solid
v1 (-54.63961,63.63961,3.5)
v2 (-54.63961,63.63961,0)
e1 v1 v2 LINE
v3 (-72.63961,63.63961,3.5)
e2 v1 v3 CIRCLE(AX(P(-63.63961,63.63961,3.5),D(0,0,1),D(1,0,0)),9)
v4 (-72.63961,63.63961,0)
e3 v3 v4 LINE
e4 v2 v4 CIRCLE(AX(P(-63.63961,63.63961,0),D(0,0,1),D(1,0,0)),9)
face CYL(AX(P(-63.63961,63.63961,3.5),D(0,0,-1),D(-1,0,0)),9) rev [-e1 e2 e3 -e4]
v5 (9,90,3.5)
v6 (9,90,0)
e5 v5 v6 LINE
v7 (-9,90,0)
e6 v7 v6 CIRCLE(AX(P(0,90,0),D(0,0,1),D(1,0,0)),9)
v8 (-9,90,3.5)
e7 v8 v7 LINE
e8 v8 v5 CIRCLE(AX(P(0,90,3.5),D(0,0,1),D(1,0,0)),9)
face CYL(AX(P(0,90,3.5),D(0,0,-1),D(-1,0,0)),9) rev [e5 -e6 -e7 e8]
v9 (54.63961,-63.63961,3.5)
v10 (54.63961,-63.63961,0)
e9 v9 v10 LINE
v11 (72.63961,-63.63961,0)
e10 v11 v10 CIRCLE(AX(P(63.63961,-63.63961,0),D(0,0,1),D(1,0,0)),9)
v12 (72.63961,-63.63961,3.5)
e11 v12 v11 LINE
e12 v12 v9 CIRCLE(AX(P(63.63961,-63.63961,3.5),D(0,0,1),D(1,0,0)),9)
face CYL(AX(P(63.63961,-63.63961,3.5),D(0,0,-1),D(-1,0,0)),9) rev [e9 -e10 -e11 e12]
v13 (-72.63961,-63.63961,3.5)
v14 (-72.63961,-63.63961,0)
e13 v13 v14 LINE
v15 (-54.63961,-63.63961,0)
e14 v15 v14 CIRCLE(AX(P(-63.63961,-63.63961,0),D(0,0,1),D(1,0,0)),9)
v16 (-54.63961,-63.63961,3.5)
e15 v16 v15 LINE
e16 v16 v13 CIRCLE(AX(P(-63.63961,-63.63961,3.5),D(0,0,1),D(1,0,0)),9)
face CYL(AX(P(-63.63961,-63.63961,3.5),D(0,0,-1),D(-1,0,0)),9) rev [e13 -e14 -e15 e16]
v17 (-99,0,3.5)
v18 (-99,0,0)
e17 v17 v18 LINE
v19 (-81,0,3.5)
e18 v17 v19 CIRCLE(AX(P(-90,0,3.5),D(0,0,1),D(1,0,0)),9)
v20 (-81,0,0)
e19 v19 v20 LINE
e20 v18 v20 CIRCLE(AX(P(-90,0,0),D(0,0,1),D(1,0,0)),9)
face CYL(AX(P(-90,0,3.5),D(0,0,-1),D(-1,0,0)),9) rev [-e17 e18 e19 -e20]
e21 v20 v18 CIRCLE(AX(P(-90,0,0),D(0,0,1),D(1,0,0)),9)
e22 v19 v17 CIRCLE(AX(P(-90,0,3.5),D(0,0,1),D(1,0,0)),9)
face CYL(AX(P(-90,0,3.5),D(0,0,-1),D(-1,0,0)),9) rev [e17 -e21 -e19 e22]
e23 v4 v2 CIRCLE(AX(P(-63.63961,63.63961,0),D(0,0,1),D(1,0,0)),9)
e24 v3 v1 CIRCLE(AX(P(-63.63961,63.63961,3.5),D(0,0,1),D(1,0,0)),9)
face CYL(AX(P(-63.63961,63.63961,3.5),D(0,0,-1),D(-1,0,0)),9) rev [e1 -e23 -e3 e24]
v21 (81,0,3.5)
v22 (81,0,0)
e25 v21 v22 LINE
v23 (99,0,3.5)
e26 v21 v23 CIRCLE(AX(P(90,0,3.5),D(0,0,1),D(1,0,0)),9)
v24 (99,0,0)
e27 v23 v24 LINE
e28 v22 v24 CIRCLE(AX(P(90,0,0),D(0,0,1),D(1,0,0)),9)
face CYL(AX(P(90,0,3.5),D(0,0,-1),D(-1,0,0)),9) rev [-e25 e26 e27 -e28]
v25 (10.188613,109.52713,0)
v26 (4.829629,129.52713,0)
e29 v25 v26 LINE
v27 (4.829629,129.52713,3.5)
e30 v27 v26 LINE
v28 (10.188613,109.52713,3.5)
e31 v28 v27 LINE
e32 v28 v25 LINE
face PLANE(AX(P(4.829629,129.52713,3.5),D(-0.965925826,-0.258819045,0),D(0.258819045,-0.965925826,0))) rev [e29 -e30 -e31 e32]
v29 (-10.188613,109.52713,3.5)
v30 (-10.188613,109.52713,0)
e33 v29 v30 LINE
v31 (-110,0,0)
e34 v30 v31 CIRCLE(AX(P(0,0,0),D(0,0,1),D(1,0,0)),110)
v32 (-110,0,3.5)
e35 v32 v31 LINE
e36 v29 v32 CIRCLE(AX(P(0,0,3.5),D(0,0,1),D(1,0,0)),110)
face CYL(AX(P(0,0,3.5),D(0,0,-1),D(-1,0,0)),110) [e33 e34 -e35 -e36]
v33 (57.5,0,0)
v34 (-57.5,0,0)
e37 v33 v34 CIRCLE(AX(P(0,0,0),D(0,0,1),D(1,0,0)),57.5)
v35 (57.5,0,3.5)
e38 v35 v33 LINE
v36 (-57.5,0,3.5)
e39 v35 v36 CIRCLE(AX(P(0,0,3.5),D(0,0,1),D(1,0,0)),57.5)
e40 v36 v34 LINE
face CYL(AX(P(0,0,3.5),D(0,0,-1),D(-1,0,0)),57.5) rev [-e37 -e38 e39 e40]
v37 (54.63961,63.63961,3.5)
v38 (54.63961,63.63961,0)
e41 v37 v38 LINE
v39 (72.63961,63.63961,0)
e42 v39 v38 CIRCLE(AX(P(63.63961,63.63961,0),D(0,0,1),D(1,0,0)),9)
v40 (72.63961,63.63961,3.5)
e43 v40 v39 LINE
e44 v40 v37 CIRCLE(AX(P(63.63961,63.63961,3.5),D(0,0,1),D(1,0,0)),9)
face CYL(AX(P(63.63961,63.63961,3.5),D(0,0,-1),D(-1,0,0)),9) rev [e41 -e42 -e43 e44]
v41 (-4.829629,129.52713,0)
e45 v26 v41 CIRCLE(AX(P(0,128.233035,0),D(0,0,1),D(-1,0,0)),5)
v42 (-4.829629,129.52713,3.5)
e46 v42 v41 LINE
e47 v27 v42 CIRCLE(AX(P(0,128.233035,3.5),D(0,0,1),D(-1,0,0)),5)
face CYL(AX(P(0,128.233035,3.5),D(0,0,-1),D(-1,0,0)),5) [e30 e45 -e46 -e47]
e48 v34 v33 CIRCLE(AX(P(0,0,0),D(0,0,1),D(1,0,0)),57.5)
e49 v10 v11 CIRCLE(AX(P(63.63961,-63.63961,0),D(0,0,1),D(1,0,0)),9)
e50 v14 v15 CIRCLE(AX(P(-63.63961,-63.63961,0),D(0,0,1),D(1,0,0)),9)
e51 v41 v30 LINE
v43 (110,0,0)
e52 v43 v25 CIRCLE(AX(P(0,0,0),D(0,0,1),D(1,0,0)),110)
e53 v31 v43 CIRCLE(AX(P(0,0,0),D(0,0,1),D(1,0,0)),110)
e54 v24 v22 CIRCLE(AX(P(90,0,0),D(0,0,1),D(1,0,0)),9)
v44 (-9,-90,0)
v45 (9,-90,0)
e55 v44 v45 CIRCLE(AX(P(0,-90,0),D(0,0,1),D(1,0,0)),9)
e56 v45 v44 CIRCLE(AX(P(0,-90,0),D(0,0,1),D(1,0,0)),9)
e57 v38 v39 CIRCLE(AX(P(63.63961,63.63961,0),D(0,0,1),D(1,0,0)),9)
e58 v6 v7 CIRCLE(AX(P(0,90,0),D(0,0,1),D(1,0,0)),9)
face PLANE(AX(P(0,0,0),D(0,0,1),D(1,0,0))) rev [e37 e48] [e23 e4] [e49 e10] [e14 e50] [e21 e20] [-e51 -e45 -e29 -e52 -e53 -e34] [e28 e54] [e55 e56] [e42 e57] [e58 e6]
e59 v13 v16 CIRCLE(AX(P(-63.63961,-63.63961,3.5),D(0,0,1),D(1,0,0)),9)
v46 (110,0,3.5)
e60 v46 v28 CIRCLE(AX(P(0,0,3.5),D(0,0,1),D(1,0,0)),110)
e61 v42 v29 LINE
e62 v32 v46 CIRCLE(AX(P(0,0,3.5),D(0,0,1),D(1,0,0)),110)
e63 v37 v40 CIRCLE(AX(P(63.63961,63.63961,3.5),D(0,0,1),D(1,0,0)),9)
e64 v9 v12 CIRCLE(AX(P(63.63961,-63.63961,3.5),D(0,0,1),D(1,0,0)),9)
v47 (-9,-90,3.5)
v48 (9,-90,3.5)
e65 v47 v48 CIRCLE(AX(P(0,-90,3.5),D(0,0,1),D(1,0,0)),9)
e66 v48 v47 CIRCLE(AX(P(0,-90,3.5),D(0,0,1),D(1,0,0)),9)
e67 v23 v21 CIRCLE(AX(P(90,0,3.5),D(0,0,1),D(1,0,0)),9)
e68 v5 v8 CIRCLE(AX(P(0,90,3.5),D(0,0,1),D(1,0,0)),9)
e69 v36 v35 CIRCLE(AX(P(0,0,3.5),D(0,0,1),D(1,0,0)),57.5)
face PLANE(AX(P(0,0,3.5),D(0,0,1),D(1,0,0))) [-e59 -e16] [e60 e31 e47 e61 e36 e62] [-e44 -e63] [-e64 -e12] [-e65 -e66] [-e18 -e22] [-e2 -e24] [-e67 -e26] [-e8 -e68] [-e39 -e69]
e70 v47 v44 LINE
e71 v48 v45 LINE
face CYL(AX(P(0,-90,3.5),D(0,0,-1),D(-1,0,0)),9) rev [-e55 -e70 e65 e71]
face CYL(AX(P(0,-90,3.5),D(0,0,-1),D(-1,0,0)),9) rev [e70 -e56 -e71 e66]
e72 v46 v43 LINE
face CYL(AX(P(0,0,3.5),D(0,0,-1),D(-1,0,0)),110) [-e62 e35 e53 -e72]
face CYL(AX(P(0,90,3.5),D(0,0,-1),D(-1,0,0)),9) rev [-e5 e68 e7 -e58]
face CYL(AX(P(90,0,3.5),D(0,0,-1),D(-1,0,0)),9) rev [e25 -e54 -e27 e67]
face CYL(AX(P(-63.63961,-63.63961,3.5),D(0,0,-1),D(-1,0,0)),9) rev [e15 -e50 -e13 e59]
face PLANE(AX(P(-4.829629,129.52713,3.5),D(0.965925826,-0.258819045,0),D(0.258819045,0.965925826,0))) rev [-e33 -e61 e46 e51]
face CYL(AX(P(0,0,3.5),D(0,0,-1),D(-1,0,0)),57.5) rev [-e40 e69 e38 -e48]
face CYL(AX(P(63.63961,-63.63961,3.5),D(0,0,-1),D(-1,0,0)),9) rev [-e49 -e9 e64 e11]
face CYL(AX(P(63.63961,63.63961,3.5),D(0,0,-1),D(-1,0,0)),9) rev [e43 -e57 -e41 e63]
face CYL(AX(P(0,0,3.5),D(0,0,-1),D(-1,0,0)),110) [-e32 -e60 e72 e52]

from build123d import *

# Parameters (mm, degrees)
SKETCH1_R           = 57.5
SKETCH1_R_2         = 9
BOSS_EXTRUDE1_DEPTH = 3.5


with BuildPart() as part:
    # Sketch1 → Boss-Extrude1 (new body)
    with BuildSketch(Plane.XY):
        with BuildLine():
            Line((-4.829629131, 129.527129815), (-10.18861298, 109.527129815))
            ThreePointArc((-10.18861298, 109.527129815), (0, -110), (10.18861298, 109.527129815))
            Line((10.18861298, 109.527129815), (4.829629131, 129.527129815))
            ThreePointArc((4.829629131, 129.527129815), (0, 133.23303459), (-4.829629131, 129.527129815))
        make_face()
        Circle(SKETCH1_R, mode=Mode.SUBTRACT)
        with Locations((0, 90)):
            Circle(SKETCH1_R_2, mode=Mode.SUBTRACT)
        with Locations((63.639610307, 63.639610307)):
            Circle(SKETCH1_R_2, mode=Mode.SUBTRACT)
        with Locations((90, 0)):
            Circle(SKETCH1_R_2, mode=Mode.SUBTRACT)
        with Locations((63.639610307, -63.639610307)):
            Circle(SKETCH1_R_2, mode=Mode.SUBTRACT)
        with Locations((0, -90)):
            Circle(SKETCH1_R_2, mode=Mode.SUBTRACT)
        with Locations((-63.639610307, -63.639610307)):
            Circle(SKETCH1_R_2, mode=Mode.SUBTRACT)
        with Locations((-90, 0)):
            Circle(SKETCH1_R_2, mode=Mode.SUBTRACT)
        with Locations((-63.639610307, 63.639610307)):
            Circle(SKETCH1_R_2, mode=Mode.SUBTRACT)
    extrude(amount=BOSS_EXTRUDE1_DEPTH)


solid = part.part
